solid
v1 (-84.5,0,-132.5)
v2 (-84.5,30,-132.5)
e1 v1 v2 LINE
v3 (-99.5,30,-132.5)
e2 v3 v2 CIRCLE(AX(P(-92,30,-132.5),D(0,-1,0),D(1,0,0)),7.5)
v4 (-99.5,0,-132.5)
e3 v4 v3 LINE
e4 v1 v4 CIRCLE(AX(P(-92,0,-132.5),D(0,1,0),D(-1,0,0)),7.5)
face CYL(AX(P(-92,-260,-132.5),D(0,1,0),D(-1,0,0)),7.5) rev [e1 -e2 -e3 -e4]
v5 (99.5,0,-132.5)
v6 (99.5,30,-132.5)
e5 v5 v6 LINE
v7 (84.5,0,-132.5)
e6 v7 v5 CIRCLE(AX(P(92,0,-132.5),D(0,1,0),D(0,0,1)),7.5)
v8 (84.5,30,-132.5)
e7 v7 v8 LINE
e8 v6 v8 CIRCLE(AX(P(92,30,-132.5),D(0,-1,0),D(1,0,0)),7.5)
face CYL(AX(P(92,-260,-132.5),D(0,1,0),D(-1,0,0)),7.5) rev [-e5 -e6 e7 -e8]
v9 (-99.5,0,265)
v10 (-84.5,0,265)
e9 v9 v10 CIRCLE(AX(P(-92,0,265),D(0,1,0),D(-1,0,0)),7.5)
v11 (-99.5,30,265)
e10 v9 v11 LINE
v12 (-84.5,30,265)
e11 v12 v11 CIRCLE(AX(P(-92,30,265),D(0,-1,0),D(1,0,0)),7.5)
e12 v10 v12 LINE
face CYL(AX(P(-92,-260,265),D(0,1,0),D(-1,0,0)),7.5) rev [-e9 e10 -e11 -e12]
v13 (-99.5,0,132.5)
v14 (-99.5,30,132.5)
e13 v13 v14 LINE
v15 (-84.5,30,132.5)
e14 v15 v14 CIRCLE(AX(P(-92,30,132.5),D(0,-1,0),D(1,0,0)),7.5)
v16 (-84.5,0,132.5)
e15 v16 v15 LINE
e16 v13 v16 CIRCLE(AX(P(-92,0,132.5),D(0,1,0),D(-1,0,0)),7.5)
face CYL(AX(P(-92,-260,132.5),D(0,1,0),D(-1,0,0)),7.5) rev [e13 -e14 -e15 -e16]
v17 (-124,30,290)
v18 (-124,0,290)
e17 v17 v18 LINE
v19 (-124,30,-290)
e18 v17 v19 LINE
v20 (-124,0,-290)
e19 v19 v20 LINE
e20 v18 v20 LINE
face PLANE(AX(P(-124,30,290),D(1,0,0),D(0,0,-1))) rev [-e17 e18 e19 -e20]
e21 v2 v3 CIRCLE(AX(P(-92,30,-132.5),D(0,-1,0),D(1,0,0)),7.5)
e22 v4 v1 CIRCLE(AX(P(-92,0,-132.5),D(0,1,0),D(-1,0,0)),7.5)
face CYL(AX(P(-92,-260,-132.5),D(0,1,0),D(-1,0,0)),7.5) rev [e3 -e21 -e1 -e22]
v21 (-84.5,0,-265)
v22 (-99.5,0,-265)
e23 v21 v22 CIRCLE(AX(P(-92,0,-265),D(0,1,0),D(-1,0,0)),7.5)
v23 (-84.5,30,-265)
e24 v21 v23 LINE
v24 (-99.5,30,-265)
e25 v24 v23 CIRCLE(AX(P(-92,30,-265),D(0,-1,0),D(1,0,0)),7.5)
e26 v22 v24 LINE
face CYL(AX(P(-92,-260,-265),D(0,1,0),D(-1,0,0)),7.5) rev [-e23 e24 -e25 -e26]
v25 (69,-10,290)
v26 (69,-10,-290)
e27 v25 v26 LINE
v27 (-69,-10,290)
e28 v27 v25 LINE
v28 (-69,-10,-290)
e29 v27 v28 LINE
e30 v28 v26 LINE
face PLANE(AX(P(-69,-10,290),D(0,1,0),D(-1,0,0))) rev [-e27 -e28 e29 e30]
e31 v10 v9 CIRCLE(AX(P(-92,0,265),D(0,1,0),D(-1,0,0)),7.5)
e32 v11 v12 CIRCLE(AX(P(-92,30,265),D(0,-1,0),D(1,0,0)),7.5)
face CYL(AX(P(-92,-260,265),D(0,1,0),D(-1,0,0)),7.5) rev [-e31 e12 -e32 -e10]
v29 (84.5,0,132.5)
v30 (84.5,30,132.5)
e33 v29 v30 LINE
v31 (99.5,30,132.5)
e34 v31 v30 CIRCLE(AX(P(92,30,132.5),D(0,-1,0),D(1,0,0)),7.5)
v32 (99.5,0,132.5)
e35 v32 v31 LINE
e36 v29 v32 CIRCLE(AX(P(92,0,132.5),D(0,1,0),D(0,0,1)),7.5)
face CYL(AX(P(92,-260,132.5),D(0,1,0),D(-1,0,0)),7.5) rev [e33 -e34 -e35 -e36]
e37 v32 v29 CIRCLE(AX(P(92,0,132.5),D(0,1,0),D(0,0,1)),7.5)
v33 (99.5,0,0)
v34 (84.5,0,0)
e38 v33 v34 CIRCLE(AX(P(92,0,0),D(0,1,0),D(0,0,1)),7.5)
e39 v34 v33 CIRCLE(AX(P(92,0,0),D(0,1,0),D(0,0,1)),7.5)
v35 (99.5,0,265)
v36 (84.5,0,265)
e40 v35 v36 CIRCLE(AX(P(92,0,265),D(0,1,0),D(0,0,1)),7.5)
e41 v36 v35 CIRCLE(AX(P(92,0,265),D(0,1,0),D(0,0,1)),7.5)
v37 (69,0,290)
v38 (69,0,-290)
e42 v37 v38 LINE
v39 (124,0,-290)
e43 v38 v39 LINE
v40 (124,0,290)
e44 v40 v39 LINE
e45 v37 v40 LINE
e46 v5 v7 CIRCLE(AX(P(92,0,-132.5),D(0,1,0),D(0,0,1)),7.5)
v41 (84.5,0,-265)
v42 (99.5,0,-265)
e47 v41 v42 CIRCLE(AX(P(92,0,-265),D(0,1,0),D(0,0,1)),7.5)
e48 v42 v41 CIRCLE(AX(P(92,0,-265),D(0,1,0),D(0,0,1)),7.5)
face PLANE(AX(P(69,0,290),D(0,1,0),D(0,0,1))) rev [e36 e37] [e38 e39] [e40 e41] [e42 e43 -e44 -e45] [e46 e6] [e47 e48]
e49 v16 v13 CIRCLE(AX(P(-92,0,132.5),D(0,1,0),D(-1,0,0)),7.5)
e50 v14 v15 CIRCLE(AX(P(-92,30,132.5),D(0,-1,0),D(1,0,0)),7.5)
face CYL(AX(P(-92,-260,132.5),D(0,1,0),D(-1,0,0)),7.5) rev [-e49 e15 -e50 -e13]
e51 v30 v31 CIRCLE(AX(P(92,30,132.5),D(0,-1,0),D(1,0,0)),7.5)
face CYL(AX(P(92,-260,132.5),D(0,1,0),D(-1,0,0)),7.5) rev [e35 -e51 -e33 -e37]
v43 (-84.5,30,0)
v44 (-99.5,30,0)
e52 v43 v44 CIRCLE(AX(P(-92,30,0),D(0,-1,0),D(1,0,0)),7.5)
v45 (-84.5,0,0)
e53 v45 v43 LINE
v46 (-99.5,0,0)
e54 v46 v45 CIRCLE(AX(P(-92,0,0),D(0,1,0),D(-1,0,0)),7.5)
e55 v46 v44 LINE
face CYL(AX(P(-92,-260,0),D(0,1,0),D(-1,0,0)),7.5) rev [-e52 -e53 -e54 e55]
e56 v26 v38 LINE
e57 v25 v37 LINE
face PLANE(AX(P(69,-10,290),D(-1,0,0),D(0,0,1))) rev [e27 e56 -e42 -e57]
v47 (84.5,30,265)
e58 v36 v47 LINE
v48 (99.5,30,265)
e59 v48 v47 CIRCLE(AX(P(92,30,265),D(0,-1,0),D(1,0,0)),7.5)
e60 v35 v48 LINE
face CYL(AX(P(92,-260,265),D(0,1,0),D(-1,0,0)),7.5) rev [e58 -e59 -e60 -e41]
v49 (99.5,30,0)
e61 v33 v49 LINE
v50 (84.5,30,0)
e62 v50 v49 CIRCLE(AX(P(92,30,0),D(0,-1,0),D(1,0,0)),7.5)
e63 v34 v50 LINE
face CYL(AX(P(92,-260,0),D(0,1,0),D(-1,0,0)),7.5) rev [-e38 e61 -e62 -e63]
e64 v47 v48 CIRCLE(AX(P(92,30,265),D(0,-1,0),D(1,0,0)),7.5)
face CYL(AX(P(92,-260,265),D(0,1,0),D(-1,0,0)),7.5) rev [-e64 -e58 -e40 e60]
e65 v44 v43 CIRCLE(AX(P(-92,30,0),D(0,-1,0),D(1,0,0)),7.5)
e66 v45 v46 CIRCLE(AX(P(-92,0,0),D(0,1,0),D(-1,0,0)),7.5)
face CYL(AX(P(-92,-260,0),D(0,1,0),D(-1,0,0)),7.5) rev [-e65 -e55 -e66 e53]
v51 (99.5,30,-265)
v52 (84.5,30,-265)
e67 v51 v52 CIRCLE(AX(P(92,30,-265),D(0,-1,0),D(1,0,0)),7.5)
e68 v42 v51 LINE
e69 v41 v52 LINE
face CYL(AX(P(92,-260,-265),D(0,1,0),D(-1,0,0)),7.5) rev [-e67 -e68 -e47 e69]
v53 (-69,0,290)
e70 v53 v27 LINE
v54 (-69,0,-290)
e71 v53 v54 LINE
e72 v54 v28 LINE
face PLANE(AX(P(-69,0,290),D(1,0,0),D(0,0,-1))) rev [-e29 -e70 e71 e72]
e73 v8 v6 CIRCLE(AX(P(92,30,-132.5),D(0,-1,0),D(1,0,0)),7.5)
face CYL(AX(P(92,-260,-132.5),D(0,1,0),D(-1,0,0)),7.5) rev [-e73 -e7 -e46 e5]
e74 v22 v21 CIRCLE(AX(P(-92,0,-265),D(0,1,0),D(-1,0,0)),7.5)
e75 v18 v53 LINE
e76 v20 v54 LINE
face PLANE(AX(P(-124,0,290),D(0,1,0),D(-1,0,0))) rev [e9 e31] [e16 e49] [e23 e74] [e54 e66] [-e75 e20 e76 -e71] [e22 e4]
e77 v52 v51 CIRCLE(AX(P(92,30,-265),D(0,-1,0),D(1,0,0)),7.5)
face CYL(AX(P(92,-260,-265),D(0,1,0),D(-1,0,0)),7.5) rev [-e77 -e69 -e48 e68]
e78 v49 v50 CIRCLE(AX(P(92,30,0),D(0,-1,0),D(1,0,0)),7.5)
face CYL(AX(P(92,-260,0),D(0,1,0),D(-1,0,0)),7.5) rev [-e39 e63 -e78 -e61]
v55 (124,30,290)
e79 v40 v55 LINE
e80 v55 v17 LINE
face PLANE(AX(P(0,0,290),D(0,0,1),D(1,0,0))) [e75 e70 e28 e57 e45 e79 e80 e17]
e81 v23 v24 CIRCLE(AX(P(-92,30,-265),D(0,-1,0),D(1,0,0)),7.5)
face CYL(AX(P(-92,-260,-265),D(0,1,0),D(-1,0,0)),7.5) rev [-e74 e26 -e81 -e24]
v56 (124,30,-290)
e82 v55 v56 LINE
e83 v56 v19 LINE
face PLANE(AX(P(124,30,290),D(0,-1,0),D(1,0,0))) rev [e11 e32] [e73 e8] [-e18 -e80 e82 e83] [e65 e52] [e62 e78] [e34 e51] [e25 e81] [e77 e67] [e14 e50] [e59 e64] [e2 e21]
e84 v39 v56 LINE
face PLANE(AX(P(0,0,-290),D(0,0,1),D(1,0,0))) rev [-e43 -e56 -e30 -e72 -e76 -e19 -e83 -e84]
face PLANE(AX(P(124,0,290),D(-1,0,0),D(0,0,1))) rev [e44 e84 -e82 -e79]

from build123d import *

# Parameters (mm, degrees)
BASE_PLATE_DEPTH            = 290
MOUNTING_HOLES_SKETCH_R     = 7.5
MOUNTING_HOLES_10X_15_DEPTH = 290


with BuildPart() as part:
    # Plate Profile Sketch → Base Plate (new, symmetric)
    with BuildSketch(Plane.XY):
        Polygon((-124, 0), (-69, 0), (-69, -10), (69, -10), (69, 0), (124, 0), (124, 30), (-124, 30), align=None)
    extrude(amount=BASE_PLATE_DEPTH, both=True)

    # Mounting Holes Sketch → Mounting Holes 10xØ15 (cut, symmetric)
    with BuildSketch(Plane(origin=(0, 30, 0), x_dir=(1, 0, 0), z_dir=(0, 1, 0))):
        with Locations(Location((-92, 265, 0), (0, 0, 180))):
            Circle(MOUNTING_HOLES_SKETCH_R)
        with Locations(Location((-92, 132.5, 0), (0, 0, 180))):
            Circle(MOUNTING_HOLES_SKETCH_R)
        with Locations(Location((-92, 0, 0), (0, 0, 180))):
            Circle(MOUNTING_HOLES_SKETCH_R)
        with Locations(Location((-92, -132.5, 0), (0, 0, 180))):
            Circle(MOUNTING_HOLES_SKETCH_R)
        with Locations(Location((-92, -265, 0), (0, 0, 180))):
            Circle(MOUNTING_HOLES_SKETCH_R)
        with Locations(Location((92, 132.5, 0), (0, 0, 270))):
            Circle(MOUNTING_HOLES_SKETCH_R)
        with Locations(Location((92, 0, 0), (0, 0, 270))):
            Circle(MOUNTING_HOLES_SKETCH_R)
        with Locations(Location((92, -132.5, 0), (0, 0, 270))):
            Circle(MOUNTING_HOLES_SKETCH_R)
        with Locations(Location((92, -265, 0), (0, 0, 270))):
            Circle(MOUNTING_HOLES_SKETCH_R)
        with Locations(Location((92, 265, 0), (0, 0, 270))):
            Circle(MOUNTING_HOLES_SKETCH_R)
    extrude(amount=MOUNTING_HOLES_10X_15_DEPTH, both=True, mode=Mode.SUBTRACT)


solid = part.part
